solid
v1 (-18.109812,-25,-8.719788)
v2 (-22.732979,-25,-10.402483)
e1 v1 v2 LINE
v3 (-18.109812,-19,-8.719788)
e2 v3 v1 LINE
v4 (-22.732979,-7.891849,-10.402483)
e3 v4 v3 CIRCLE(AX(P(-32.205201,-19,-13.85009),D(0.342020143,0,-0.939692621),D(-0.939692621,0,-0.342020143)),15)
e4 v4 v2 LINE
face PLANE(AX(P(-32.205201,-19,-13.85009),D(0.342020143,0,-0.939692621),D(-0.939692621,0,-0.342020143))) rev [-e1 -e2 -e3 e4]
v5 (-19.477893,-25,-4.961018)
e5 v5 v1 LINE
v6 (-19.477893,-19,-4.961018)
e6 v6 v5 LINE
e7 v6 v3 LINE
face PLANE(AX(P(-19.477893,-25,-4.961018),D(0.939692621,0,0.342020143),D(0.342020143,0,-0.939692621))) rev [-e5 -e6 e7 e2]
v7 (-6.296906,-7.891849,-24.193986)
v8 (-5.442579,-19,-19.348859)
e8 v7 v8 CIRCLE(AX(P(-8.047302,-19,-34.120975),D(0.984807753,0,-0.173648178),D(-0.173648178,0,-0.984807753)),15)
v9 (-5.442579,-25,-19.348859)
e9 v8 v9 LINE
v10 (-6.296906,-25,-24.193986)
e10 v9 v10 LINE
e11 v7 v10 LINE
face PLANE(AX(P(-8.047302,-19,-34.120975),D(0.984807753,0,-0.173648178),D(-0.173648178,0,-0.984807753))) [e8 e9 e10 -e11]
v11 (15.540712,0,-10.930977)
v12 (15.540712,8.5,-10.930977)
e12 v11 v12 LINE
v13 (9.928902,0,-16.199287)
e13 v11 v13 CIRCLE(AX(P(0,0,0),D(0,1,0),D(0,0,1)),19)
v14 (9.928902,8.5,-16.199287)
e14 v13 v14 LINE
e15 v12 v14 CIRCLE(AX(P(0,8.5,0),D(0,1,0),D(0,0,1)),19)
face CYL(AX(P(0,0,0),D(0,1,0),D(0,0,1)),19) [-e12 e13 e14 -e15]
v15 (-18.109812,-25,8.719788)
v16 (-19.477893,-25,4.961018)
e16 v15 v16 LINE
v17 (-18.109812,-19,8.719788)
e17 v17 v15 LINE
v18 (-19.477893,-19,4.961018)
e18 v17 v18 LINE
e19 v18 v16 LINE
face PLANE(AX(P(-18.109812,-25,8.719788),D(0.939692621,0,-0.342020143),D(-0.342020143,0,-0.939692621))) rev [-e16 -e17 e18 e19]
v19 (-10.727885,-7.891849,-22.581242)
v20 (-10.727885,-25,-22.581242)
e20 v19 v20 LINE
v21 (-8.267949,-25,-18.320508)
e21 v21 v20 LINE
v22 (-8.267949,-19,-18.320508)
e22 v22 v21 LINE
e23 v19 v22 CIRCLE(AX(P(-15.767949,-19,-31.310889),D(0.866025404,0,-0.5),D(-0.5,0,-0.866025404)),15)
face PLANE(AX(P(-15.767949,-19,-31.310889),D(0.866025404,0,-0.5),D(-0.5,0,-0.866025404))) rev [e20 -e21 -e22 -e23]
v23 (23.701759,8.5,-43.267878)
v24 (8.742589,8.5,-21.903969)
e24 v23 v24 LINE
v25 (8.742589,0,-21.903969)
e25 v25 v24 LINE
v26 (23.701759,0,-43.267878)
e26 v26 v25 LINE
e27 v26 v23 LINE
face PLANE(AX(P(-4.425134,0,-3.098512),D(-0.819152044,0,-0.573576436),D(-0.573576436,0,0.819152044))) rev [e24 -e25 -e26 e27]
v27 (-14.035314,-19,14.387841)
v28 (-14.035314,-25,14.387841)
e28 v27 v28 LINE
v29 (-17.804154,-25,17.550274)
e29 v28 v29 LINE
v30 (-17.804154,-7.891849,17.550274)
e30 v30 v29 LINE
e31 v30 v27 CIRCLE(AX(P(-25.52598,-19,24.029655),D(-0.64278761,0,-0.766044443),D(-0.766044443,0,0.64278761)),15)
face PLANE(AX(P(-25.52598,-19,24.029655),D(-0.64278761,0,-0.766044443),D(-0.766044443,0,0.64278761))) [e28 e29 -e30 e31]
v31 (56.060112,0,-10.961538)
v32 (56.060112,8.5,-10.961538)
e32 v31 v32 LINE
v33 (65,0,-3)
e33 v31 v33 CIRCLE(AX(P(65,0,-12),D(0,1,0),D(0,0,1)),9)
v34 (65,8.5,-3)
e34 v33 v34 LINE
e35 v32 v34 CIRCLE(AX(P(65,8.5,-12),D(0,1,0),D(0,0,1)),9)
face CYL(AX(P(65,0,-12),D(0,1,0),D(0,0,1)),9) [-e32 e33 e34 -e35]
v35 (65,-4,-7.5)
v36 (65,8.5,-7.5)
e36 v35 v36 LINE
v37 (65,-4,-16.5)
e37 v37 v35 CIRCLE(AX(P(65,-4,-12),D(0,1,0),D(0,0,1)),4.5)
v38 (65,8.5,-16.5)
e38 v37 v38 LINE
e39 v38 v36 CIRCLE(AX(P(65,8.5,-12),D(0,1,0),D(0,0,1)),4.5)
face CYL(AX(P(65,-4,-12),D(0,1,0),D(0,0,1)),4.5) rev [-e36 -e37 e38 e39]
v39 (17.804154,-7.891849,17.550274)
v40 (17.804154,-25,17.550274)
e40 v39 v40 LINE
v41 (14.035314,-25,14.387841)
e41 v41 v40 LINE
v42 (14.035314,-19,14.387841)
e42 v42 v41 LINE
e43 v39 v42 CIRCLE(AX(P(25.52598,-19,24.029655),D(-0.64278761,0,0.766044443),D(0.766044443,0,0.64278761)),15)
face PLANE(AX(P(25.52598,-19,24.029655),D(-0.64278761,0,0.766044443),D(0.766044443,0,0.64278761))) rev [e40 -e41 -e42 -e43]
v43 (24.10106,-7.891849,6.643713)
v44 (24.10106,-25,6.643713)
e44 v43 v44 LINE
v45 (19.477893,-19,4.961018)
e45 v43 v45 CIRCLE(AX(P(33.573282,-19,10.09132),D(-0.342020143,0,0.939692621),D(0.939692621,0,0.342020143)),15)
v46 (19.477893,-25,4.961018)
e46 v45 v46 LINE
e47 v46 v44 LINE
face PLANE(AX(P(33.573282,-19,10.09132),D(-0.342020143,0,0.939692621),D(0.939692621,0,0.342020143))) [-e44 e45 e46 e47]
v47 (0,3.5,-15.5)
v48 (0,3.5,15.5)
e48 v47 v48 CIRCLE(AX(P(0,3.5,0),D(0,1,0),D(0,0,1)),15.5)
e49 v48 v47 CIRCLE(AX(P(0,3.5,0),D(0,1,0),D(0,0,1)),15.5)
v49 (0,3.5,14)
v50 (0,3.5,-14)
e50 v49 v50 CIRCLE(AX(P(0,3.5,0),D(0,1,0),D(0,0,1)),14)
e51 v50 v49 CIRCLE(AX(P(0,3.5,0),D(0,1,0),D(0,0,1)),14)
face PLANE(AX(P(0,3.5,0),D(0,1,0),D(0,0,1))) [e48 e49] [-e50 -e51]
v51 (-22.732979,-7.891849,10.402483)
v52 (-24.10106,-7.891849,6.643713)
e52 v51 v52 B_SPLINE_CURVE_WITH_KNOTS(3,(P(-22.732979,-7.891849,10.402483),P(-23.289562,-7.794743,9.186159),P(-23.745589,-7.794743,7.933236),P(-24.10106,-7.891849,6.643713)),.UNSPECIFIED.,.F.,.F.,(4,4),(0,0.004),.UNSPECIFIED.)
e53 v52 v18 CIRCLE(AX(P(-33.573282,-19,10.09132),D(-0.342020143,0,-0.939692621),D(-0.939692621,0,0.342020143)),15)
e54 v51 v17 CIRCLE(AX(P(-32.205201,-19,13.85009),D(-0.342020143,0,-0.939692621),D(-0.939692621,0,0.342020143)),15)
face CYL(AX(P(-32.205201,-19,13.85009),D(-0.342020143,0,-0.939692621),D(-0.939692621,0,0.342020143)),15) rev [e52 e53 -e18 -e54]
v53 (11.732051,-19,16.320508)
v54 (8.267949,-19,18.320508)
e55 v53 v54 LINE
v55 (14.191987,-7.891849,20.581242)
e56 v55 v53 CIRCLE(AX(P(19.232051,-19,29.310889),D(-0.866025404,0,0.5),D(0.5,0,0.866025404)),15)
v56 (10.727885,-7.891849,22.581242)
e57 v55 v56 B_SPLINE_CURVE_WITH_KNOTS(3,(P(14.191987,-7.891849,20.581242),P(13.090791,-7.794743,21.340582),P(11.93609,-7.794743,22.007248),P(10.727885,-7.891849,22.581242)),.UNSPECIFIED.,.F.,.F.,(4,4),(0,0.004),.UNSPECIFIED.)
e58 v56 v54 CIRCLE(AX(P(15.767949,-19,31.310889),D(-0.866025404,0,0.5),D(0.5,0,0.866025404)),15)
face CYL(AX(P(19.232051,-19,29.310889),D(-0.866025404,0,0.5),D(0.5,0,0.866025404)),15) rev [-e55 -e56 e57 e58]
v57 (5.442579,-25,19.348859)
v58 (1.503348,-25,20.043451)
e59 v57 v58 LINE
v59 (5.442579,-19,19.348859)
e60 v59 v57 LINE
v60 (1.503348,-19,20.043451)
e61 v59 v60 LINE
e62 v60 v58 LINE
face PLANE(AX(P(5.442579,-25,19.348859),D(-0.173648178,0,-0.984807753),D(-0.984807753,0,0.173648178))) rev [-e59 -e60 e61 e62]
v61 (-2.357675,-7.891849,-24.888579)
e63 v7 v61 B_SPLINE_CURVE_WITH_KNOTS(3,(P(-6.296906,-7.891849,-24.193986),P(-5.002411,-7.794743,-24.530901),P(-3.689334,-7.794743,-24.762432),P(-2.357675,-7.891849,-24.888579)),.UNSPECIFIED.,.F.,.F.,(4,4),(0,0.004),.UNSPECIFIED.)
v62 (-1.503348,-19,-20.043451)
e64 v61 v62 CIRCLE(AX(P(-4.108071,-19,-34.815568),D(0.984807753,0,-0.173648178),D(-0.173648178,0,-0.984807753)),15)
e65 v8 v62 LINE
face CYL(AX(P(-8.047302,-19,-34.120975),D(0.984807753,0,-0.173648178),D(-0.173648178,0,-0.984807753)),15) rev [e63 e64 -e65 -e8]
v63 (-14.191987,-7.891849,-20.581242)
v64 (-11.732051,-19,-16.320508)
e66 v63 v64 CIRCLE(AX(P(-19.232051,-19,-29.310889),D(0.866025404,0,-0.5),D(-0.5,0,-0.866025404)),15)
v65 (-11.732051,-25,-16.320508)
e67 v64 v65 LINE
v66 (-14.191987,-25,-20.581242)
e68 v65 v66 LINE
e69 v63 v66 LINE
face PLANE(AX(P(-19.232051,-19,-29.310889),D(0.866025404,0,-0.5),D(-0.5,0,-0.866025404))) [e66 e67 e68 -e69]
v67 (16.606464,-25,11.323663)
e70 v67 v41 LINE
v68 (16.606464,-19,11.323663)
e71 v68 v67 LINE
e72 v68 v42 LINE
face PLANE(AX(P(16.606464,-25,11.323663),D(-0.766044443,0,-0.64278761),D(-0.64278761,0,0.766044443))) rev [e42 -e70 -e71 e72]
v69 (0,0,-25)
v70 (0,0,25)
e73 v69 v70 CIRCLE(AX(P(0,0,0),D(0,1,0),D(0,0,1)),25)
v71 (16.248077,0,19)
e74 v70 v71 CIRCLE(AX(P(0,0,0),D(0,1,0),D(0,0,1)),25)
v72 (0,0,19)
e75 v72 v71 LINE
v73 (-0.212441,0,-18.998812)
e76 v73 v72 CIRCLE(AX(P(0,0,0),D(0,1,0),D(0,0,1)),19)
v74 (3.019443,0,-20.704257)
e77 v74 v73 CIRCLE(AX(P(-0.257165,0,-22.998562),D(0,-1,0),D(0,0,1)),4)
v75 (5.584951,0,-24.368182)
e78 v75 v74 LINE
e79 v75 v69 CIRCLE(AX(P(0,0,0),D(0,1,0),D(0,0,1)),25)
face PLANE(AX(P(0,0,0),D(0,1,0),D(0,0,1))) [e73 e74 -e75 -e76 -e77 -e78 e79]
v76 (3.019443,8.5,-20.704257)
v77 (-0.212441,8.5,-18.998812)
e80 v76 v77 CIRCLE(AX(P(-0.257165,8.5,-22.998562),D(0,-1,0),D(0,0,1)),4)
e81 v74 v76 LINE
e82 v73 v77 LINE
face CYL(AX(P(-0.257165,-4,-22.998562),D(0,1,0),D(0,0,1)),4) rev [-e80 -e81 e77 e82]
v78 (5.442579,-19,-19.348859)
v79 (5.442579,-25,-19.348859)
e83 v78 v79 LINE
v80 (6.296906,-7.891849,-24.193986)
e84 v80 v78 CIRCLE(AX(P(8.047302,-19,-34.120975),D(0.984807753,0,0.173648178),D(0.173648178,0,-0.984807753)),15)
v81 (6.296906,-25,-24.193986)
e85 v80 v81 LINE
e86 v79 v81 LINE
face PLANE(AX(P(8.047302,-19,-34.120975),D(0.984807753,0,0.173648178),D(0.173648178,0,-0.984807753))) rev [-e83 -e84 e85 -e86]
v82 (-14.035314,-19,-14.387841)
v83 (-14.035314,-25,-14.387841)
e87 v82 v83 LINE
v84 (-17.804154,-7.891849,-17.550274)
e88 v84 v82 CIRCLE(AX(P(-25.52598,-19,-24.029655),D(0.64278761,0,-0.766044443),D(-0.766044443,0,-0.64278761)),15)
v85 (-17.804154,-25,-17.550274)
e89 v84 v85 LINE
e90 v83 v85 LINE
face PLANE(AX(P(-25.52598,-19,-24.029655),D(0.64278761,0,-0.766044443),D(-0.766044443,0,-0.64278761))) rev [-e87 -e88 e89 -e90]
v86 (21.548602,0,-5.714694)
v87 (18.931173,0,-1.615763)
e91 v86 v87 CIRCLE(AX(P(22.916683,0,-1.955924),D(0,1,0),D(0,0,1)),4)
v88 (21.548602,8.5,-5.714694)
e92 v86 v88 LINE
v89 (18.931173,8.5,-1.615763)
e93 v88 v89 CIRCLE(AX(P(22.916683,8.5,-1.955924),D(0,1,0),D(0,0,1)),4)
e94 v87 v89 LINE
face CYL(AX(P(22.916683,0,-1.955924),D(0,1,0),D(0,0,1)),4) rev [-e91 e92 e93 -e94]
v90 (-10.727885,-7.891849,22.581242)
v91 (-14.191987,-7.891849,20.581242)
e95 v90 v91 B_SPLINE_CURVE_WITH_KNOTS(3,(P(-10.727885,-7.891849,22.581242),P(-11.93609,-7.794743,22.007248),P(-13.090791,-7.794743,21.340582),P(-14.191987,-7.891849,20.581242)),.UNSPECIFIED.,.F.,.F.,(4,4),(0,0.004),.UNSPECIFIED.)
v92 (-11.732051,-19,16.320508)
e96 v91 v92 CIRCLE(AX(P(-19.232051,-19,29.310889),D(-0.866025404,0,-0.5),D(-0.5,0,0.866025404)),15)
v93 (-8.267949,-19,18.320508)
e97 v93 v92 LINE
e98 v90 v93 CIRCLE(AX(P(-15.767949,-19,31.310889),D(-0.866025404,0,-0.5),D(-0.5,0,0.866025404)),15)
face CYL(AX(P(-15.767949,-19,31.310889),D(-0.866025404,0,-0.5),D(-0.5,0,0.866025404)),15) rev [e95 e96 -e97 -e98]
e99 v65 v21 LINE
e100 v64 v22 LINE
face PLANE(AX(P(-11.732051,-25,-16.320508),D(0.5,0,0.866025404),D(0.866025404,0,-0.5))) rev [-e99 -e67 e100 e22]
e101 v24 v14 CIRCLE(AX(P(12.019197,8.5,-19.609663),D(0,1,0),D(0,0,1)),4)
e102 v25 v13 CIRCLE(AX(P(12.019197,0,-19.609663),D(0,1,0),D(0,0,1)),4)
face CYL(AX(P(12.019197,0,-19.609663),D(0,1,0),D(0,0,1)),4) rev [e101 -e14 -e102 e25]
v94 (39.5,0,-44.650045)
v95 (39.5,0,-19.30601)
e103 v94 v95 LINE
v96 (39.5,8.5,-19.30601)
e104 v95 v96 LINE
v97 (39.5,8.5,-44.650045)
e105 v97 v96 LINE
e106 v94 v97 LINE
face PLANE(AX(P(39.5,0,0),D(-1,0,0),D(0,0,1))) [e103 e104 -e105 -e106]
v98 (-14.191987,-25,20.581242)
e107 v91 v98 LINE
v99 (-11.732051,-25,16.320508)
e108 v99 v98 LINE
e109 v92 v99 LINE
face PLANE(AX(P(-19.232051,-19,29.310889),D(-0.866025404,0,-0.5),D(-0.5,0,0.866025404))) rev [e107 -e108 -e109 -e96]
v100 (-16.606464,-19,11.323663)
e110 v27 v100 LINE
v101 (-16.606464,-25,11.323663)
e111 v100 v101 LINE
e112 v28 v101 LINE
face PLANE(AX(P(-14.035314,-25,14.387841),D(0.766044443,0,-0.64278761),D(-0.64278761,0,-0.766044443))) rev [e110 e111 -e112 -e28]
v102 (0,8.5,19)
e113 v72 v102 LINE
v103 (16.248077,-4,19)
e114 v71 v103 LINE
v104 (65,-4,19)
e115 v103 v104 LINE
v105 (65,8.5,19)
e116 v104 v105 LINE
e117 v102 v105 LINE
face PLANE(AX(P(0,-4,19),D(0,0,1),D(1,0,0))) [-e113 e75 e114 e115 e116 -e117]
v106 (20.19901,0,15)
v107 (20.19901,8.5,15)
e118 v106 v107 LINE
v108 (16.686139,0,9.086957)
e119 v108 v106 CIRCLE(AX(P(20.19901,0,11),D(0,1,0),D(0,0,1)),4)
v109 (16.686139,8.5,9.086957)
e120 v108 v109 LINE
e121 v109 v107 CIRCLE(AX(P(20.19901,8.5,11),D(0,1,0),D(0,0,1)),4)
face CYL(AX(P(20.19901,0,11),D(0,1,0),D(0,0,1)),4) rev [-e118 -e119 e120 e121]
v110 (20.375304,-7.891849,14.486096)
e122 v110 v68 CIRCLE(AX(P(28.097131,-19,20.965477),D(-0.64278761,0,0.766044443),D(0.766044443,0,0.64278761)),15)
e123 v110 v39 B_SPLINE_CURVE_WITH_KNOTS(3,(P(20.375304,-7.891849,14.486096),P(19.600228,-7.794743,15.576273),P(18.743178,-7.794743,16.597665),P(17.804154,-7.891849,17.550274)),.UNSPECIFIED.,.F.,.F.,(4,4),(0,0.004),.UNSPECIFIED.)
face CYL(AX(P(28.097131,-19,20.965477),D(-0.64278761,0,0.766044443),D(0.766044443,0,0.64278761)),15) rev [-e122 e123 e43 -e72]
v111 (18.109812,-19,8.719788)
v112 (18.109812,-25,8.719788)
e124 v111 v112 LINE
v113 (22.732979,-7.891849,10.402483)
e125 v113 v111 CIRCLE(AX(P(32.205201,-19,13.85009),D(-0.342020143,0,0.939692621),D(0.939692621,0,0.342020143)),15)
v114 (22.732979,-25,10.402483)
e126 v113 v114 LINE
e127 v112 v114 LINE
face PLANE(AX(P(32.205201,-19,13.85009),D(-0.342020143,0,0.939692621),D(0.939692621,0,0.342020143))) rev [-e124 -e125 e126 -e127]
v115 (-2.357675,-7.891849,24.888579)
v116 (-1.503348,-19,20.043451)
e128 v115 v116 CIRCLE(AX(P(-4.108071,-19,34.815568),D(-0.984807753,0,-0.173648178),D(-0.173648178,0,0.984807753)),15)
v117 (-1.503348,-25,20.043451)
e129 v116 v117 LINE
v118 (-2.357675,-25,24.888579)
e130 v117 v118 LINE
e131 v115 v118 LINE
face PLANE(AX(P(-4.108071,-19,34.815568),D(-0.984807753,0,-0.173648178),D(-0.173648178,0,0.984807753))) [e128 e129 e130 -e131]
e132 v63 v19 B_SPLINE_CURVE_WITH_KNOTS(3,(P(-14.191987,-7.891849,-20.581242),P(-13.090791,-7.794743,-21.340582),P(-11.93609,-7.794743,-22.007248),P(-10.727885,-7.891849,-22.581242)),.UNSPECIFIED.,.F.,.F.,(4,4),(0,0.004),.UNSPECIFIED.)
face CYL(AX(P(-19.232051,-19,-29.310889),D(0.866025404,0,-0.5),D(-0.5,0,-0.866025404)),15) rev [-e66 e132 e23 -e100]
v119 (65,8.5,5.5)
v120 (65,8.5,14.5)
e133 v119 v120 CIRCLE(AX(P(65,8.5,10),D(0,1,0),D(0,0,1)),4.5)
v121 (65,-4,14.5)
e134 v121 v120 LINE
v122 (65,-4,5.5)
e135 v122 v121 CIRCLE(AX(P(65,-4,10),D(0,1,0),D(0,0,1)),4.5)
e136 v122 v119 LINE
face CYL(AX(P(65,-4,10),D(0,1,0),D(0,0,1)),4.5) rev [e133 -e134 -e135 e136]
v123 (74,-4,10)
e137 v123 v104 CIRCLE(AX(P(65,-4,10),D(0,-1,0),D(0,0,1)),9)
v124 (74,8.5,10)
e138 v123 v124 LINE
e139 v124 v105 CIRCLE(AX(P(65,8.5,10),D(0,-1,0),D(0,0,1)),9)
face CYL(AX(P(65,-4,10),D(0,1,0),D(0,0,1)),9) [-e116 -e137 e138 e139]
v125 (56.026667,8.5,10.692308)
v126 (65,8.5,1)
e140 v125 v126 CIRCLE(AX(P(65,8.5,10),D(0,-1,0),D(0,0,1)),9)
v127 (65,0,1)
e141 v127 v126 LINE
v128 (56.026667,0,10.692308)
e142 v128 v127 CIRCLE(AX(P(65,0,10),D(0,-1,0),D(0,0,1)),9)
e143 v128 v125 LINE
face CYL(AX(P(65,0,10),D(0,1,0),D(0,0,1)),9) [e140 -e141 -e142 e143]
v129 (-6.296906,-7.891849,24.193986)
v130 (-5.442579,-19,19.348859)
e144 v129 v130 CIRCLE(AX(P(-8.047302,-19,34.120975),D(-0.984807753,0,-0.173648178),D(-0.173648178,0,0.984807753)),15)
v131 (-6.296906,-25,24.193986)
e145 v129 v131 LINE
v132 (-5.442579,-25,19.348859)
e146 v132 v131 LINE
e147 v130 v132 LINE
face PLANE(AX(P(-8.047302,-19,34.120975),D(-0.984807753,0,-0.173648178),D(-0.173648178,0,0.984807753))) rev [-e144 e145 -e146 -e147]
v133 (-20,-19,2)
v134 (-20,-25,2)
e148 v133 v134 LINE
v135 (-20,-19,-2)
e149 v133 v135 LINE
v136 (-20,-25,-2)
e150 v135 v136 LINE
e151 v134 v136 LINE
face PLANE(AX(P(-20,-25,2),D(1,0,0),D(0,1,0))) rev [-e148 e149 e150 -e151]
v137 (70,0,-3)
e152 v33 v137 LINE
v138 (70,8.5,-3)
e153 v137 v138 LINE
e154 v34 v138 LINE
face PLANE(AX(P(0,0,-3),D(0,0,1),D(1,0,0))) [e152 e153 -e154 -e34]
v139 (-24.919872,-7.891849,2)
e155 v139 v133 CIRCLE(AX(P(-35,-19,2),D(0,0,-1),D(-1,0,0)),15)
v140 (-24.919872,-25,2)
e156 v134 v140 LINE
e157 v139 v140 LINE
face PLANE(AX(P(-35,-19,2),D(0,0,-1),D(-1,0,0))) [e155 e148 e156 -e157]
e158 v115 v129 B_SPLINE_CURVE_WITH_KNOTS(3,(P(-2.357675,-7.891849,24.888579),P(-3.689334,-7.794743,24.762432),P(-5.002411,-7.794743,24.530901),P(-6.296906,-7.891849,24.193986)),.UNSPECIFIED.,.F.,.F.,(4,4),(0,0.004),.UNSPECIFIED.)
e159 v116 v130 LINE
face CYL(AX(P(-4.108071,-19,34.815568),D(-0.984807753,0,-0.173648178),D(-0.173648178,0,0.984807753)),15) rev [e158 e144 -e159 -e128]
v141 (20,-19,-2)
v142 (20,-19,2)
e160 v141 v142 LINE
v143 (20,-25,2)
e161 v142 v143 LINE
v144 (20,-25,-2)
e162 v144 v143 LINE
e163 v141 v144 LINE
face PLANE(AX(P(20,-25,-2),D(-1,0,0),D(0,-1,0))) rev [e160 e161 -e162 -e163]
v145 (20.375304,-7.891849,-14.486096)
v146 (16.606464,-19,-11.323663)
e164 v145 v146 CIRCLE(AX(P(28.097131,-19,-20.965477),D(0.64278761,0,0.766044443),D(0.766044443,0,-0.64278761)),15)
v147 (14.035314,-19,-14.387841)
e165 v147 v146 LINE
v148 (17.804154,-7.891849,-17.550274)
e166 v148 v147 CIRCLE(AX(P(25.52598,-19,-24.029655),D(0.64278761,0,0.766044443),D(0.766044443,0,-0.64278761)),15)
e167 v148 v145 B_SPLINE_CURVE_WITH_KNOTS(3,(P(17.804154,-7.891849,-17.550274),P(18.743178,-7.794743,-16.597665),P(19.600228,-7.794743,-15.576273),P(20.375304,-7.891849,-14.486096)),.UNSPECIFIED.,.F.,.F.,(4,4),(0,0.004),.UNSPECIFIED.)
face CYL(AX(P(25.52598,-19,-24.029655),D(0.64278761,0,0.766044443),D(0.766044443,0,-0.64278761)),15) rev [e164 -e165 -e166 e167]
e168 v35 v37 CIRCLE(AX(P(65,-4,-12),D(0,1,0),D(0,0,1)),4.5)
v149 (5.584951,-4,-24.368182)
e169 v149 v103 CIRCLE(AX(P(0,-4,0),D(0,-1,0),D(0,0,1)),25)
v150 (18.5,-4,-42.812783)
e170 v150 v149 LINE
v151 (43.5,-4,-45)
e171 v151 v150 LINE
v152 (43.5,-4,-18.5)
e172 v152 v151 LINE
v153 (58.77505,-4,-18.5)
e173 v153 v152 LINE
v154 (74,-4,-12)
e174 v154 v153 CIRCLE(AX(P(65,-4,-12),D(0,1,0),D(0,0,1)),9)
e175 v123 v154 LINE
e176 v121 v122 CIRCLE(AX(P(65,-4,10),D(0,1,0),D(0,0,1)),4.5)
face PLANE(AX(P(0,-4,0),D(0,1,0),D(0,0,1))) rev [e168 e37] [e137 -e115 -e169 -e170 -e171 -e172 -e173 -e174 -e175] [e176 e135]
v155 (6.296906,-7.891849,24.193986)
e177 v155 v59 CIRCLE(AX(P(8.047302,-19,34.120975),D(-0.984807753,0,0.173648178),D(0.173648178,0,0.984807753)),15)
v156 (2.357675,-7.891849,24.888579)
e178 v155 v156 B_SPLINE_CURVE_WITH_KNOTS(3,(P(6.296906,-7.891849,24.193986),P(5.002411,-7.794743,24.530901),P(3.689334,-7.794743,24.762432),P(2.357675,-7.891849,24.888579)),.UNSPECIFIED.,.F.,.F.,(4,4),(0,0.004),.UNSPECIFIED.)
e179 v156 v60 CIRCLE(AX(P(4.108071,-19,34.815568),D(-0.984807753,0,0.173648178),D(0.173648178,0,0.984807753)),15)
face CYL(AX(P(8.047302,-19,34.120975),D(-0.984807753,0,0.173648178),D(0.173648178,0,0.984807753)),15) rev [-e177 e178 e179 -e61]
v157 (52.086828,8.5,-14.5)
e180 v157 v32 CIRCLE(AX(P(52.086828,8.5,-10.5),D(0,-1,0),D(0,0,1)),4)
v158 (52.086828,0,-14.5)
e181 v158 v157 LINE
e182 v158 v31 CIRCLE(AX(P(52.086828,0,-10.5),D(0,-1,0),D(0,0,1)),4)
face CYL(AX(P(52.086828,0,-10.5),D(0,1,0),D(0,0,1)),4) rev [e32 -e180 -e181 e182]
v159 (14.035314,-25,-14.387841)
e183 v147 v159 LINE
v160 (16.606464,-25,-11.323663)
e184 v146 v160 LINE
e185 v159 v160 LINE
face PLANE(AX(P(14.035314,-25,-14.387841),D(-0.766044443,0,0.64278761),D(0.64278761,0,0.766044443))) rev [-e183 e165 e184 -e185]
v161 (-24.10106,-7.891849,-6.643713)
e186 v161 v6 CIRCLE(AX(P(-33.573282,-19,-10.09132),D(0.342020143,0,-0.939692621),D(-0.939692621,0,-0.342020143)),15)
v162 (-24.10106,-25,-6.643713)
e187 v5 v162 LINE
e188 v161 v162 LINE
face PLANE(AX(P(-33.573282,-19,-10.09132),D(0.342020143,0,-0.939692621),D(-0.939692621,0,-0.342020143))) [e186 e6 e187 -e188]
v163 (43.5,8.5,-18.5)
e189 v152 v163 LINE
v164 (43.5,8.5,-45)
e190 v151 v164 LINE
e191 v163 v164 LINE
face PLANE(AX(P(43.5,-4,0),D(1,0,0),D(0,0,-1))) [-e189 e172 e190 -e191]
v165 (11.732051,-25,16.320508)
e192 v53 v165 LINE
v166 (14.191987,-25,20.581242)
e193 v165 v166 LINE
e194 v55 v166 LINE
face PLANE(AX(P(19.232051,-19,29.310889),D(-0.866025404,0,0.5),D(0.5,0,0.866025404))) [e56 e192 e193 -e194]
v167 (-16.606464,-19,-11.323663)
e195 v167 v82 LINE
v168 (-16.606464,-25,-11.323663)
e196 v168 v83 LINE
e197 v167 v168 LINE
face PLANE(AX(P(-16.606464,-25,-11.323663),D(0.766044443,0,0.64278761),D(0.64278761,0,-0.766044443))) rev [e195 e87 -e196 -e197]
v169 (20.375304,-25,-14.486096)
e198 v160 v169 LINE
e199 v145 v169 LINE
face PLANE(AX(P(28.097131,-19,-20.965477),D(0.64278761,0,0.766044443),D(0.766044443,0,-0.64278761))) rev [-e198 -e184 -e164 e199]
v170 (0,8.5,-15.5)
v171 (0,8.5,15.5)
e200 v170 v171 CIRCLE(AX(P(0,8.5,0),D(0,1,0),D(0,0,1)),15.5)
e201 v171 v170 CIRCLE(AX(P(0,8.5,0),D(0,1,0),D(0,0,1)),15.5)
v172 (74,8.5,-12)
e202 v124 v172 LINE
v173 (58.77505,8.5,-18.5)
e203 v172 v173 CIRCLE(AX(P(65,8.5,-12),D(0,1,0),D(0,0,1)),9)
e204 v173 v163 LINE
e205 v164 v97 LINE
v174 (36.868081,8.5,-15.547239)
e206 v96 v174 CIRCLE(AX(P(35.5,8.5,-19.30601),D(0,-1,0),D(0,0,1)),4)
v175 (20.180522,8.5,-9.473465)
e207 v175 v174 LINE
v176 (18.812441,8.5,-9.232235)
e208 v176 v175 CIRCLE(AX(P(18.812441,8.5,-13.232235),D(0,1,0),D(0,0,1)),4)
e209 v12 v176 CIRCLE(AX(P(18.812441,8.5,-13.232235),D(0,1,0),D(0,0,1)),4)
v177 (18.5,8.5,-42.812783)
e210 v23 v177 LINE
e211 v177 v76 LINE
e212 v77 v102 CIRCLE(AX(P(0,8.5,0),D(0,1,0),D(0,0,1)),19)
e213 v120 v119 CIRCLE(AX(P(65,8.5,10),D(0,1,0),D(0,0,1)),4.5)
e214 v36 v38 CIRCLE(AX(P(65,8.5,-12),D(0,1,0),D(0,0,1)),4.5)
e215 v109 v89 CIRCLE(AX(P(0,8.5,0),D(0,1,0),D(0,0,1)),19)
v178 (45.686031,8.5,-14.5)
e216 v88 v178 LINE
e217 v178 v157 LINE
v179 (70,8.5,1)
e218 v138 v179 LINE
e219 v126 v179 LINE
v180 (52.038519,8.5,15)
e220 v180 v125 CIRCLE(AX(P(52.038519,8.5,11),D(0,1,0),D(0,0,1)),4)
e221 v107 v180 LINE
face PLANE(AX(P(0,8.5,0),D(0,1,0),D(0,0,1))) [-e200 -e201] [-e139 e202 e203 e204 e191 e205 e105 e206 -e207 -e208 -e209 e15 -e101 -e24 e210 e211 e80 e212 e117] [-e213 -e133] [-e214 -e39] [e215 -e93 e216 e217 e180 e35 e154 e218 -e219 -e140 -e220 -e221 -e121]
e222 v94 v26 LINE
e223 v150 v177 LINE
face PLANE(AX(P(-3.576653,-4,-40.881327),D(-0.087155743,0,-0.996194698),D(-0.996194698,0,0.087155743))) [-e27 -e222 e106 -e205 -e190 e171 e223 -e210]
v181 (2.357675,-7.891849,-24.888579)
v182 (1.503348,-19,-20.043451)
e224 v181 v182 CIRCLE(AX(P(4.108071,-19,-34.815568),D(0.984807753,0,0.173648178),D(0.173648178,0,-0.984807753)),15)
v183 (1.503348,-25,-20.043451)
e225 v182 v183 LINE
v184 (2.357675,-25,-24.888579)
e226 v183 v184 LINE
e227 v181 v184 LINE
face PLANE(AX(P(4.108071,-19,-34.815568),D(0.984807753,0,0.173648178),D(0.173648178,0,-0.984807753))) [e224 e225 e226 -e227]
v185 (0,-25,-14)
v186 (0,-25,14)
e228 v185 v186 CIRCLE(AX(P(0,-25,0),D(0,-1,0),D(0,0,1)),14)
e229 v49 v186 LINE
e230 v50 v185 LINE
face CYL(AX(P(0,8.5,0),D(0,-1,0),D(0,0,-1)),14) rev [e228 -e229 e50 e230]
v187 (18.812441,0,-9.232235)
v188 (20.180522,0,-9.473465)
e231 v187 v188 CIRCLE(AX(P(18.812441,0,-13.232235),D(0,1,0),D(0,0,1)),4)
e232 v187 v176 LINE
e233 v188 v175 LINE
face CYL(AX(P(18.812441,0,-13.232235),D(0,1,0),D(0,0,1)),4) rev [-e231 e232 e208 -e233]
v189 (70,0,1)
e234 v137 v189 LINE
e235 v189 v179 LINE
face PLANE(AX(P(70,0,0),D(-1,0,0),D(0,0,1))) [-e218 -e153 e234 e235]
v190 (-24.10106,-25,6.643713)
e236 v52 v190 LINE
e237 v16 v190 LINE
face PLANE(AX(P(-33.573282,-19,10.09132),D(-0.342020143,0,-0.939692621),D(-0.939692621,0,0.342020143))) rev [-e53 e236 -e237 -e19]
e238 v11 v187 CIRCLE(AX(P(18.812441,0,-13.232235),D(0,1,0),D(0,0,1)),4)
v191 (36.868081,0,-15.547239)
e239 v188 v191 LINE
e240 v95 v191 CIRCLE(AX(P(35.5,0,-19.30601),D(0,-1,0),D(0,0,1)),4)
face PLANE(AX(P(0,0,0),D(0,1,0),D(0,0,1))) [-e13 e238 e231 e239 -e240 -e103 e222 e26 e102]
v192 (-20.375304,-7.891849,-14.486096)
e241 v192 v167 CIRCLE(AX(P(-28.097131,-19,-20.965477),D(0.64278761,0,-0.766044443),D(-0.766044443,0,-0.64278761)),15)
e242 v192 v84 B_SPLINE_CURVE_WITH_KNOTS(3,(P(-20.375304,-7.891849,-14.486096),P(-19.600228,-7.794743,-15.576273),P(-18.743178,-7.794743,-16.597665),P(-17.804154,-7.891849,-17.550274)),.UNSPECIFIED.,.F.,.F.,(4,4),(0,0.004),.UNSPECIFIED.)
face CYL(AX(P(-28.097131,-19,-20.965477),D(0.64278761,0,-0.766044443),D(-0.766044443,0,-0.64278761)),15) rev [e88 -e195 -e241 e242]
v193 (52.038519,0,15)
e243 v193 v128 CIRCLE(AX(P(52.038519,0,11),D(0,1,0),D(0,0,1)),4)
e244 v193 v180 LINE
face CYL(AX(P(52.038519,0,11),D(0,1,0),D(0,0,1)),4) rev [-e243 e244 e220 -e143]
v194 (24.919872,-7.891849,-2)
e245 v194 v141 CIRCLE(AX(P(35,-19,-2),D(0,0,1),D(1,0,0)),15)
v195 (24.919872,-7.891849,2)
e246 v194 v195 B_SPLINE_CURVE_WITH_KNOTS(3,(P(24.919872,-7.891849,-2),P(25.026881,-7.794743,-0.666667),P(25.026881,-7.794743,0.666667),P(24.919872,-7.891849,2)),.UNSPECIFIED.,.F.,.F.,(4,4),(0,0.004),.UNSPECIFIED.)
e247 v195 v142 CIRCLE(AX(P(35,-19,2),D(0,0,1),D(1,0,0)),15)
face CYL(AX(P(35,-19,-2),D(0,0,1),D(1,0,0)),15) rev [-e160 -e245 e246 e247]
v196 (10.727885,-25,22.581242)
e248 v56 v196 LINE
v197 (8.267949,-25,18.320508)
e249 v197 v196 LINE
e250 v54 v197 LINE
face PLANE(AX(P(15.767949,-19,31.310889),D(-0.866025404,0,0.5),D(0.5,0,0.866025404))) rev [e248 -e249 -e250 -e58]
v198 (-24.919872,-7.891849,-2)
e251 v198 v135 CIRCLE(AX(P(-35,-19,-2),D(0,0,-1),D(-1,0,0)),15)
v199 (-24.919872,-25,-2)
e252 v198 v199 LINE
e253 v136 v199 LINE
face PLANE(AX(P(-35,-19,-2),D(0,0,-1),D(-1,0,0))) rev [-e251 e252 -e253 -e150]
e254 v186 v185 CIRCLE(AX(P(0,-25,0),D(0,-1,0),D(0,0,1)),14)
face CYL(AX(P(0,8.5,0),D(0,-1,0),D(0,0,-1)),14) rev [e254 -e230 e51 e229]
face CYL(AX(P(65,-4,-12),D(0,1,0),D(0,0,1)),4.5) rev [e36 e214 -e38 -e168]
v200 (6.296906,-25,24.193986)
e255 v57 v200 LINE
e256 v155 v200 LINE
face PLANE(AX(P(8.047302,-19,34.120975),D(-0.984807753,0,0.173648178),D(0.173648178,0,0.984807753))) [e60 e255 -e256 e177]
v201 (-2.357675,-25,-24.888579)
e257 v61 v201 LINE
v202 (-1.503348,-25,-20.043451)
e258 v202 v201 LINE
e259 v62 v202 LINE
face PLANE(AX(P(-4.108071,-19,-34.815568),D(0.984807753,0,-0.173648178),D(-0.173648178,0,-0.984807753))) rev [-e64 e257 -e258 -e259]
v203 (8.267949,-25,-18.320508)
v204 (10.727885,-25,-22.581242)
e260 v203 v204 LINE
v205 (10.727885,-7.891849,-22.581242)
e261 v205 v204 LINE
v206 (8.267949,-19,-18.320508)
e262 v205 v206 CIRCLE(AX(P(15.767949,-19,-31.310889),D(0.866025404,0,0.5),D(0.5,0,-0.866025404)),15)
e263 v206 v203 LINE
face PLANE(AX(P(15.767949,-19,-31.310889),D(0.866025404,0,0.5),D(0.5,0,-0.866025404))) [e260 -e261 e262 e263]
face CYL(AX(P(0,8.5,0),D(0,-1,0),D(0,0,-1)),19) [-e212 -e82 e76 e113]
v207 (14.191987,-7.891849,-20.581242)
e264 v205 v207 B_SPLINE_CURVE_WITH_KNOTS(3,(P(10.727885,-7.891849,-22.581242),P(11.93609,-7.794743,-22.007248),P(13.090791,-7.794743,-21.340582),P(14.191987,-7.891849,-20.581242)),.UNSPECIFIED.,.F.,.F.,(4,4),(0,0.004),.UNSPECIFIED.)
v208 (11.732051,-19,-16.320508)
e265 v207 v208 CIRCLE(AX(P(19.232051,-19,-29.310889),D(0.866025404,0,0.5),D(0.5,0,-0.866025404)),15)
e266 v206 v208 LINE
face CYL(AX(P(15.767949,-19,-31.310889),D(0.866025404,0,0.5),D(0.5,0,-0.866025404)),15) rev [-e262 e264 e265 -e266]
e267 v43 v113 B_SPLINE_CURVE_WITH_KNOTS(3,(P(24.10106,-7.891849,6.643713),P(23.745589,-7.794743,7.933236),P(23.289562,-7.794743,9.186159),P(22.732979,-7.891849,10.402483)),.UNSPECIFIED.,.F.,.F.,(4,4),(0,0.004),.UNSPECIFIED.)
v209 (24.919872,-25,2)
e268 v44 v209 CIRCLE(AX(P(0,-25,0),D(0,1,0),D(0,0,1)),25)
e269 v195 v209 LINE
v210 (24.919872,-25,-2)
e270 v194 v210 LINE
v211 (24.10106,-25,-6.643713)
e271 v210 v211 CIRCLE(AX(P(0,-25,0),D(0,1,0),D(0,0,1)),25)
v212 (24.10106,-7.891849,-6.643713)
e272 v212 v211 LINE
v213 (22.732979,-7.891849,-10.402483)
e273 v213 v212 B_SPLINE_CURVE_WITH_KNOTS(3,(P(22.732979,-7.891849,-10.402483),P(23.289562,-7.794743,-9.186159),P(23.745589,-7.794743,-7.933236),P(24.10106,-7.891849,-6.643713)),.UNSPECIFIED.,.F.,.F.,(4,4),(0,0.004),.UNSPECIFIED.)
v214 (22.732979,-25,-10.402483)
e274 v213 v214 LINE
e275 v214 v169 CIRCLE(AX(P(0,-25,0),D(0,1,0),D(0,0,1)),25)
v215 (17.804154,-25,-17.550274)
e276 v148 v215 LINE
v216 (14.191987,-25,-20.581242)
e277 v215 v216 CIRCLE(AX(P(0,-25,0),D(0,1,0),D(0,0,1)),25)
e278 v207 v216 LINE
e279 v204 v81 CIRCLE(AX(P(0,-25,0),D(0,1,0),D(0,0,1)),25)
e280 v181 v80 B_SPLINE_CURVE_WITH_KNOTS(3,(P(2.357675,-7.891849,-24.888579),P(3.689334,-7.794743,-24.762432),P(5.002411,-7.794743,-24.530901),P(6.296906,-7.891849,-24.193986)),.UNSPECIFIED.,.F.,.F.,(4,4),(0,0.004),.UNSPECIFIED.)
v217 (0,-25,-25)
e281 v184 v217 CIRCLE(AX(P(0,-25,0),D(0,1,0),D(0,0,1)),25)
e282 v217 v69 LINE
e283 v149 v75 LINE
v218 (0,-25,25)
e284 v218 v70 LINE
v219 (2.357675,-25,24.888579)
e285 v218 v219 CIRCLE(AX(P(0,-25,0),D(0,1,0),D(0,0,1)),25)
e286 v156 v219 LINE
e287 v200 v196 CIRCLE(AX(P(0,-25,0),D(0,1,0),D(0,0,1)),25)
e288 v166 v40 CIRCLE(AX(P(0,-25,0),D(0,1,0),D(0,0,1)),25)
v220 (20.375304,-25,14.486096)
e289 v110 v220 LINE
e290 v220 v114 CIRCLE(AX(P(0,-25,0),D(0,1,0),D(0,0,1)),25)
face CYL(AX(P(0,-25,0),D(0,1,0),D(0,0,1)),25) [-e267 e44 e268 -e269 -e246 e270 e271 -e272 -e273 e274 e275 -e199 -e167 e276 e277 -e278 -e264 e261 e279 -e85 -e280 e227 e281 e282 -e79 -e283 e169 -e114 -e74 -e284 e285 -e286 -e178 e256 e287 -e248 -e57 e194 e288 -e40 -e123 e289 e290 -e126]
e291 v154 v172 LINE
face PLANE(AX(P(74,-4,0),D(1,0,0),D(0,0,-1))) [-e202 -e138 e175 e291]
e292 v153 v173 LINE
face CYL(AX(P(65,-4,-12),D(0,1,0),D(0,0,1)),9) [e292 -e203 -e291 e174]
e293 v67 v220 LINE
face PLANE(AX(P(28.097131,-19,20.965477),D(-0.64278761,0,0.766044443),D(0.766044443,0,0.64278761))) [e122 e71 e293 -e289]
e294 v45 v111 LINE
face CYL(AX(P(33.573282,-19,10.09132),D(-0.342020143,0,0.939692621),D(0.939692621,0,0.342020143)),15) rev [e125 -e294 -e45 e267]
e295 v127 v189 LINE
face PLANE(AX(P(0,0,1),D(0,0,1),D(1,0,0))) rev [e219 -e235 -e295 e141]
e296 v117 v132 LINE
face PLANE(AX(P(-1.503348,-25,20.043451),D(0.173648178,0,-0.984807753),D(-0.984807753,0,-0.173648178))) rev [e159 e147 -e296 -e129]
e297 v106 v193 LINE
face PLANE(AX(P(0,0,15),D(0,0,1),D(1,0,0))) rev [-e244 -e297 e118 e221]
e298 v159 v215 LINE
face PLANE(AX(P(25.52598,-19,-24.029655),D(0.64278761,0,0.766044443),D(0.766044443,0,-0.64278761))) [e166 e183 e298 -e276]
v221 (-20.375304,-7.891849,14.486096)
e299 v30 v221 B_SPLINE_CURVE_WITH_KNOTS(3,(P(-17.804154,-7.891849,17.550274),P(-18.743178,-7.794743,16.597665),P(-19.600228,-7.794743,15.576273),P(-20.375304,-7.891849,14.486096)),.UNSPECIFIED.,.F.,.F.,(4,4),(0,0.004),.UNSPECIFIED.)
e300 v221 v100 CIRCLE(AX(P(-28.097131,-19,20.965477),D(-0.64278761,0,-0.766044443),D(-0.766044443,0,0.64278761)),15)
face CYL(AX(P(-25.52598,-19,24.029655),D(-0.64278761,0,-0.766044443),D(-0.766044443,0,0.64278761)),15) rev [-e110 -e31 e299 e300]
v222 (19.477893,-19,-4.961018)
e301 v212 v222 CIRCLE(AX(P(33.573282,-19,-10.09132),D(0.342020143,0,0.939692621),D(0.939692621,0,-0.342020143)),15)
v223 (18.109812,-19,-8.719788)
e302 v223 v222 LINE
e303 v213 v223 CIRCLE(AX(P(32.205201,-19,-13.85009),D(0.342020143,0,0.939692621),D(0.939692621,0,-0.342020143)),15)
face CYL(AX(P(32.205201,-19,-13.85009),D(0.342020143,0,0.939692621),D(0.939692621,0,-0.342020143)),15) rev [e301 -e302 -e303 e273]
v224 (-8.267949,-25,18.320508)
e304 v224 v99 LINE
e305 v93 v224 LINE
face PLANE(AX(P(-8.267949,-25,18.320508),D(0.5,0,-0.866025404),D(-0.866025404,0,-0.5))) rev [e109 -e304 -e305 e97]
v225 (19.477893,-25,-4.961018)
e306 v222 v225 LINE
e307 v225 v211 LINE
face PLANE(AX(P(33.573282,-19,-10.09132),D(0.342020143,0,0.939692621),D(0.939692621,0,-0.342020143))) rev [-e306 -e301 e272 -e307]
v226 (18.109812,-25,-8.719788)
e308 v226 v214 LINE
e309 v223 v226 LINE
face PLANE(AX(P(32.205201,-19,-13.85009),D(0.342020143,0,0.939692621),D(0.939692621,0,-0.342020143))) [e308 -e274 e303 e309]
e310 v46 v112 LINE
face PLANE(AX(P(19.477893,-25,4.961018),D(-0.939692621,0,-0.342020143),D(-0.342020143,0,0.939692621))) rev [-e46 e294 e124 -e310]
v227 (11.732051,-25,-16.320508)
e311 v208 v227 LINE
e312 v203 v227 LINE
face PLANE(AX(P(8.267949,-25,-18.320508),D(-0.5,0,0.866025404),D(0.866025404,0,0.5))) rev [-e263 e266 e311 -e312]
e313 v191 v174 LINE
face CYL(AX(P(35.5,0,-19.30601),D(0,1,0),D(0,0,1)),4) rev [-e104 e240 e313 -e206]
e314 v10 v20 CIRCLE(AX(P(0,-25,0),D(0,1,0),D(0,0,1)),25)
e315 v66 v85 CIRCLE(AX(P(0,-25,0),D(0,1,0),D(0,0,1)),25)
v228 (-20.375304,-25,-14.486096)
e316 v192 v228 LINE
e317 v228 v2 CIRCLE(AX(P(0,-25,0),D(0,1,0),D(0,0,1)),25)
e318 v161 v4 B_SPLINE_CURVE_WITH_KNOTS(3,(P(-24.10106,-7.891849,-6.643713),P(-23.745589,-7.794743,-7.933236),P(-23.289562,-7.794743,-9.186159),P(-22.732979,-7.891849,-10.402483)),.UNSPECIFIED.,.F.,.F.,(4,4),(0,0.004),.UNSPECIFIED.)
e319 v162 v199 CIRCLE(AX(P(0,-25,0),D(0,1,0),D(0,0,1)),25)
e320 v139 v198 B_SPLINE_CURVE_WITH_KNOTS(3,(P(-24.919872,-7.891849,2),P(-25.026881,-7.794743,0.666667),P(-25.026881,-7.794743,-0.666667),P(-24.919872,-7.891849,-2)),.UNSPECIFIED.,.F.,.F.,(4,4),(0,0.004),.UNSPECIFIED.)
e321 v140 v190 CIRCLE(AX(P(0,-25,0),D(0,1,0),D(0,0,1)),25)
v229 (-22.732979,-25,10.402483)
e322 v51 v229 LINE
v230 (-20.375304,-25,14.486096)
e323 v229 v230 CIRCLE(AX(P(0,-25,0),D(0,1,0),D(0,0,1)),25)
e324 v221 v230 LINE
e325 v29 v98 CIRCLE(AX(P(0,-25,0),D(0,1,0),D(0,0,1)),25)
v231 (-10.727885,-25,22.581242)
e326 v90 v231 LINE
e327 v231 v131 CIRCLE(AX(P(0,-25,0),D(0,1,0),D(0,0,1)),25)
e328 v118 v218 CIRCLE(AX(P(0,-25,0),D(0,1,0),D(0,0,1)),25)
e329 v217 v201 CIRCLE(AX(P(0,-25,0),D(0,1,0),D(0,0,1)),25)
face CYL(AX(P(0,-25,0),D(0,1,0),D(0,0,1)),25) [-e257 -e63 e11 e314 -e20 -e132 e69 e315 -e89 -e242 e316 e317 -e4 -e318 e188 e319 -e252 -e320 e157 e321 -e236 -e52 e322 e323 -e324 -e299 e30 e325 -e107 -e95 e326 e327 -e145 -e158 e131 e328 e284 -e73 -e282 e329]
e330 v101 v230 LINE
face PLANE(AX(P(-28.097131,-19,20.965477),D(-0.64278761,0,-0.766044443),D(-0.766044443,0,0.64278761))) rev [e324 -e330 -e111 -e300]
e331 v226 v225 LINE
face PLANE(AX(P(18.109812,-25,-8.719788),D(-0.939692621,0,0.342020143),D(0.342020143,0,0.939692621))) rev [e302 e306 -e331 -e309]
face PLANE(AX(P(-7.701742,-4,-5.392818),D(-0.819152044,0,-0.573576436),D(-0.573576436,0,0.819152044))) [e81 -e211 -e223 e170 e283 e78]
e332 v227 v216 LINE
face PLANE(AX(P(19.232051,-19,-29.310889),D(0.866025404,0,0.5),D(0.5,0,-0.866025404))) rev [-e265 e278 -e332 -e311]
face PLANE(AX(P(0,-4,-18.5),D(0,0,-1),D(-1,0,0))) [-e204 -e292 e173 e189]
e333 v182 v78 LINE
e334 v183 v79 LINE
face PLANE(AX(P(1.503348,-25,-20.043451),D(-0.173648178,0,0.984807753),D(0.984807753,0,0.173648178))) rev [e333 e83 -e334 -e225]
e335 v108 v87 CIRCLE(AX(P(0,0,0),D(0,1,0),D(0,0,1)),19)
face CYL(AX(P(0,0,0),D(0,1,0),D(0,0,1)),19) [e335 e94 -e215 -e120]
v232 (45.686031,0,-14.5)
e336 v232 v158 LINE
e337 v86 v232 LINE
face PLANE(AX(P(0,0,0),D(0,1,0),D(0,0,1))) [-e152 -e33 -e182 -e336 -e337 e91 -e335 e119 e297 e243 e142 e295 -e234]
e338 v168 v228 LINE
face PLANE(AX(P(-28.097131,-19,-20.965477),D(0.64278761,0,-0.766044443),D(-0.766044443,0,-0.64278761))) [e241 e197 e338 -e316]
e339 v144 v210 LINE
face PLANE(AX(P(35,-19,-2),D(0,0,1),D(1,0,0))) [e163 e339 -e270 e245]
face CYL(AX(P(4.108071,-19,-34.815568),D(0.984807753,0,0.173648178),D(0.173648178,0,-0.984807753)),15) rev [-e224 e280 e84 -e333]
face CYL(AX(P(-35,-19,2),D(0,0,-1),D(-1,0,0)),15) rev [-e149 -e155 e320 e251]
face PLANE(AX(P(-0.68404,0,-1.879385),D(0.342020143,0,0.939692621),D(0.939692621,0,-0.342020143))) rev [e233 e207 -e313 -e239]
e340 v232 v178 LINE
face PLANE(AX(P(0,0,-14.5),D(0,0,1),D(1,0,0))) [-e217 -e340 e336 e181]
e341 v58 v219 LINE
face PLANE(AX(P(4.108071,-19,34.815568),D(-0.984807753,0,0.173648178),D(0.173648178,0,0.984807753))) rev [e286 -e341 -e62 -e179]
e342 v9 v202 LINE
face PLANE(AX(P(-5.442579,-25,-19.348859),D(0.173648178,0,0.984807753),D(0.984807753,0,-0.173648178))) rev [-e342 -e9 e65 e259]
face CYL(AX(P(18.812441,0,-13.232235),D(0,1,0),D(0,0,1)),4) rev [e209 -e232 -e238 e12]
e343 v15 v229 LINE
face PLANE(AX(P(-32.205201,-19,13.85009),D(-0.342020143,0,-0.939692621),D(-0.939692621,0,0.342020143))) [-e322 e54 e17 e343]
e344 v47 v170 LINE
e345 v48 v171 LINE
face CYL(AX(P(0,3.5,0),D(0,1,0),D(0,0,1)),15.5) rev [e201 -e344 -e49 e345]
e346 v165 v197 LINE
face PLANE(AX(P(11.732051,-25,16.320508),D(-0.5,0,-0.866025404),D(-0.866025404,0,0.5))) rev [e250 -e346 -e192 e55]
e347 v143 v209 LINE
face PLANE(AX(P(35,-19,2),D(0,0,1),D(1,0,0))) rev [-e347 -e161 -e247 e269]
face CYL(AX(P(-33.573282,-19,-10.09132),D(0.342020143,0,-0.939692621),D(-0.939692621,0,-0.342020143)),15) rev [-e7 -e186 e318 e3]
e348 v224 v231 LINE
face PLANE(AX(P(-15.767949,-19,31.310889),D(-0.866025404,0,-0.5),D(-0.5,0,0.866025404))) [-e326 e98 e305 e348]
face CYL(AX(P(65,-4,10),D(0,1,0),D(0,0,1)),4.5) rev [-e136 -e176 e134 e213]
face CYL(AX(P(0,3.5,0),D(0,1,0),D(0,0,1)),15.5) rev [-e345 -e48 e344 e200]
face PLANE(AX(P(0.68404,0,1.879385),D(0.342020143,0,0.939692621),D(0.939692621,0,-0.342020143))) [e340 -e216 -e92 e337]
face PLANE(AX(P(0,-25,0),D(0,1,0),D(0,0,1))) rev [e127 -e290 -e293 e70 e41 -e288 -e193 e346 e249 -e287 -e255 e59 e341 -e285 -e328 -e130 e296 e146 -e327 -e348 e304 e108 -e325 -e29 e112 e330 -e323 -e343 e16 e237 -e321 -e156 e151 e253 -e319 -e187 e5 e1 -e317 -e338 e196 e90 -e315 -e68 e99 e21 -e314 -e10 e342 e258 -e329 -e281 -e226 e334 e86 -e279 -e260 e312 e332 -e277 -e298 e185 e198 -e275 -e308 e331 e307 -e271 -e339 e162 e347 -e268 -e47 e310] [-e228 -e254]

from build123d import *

# Parameters (mm, degrees)
HUB_SKETCH_50_R                   = 25
HUB_CYLINDER_50_DEPTH             = 25
UPPER_PAD_SKETCH_R                = 19
UPPER_PAD_SKETCH_R_2              = 14
UPPER_PAD_DEPTH                   = 8.5
HUB_CUT_REACH                     = 45.301
HUB_CUT_SKETCH_R                  = 14
HUB_RECESS_SKETCH_31_R            = 15.5
HUB_RECESS_31_DEPTH               = 5
LEVER_START                       = -12.5
LEVER_ARM_PROFILE_SKETCH_R        = 4.5
LEVER_ARM_DEPTH                   = 12.5
LEVER_START_2                     = -8.5
LEVER_ARM_POCKETS_AND_HOLES_DEPTH = 8.5
FIN_SLOT_DEPTH                    = 2
FIN_SLOT_PATTERN_18X_COUNT        = 18


with BuildPart() as part:
    # Hub Sketch _50 → Hub Cylinder _50 (new body)
    with BuildSketch(Plane(origin=(0, 0, 0), x_dir=(1, 0, 0), z_dir=(0, 1, 0))):
        with Locations(Location((0, 0, 0), (0, 0, 270))):
            Circle(HUB_SKETCH_50_R)
    extrude(amount=-HUB_CYLINDER_50_DEPTH)

    # Upper Pad Sketch → Upper Pad (add)
    with BuildSketch(Plane(origin=(0, 0, 0), x_dir=(1, 0, 0), z_dir=(0, 1, 0))):
        with Locations(Location((0, 0, 0), (0, 0, 270))):
            Circle(UPPER_PAD_SKETCH_R)
        with Locations(Location((0, 0, 0), (0, 0, 270))):
            Circle(UPPER_PAD_SKETCH_R_2, mode=Mode.SUBTRACT)
    extrude(amount=UPPER_PAD_DEPTH)

    # Hub Cut Sketch → Hub Cut (cut, up to next)
    with BuildSketch(Plane(origin=(0, 0, 0), x_dir=(1, 0, 0), z_dir=(0, 1, 0)), mode=Mode.PRIVATE) as hub_cut_sk1:
        with Locations(Location((0, 0, 0), (0, 0, 270))):
            Circle(HUB_CUT_SKETCH_R)
    hub_cut_tool1 = extrude(hub_cut_sk1.sketch, amount=-HUB_CUT_REACH, mode=Mode.PRIVATE) & part.part
    add(hub_cut_tool1.solids().sort_by_distance((0, 0, 0))[0], mode=Mode.SUBTRACT)

    # Hub Recess Sketch _31 → Hub Recess _31 (cut)
    with BuildSketch(Plane(origin=(0, 8.5, 0), x_dir=(1, 0, 0), z_dir=(0, 1, 0))):
        with Locations(Location((0, 0, 0), (0, 0, 270))):
            Circle(HUB_RECESS_SKETCH_31_R)
    extrude(amount=-HUB_RECESS_31_DEPTH, mode=Mode.SUBTRACT)

    # Lever Arm Profile Sketch → Lever Arm (add)
    with BuildSketch(Plane(origin=(0, 8.5, 0), x_dir=(1, 0, 0), z_dir=(0, 1, 0)).offset(LEVER_START)):
        with BuildLine():
            Line((0, -19), (65, -19))
            ThreePointArc((65, -19), (71.363961031, -16.363961031), (74, -10))
            Line((74, -10), (74, 12))
            ThreePointArc((74, 12), (68.53379766, 20.277214151), (58.775050201, 18.5))
            Line((58.775050201, 18.5), (43.5, 18.5))
            Line((43.5, 18.5), (43.5, 45))
            Line((43.5, 45), (18.5, 42.812783412))
            Line((18.5, 42.812783412), (3.019442807, 20.704256513))
            ThreePointArc((3.019442807, 20.704256513), (1.609636047, 19.460900253), (-0.212440958, 18.998812301))
            ThreePointArc((-0.212440958, 18.998812301), (18.999703073, 0.106222139), (0, -19))
        make_face()
        with Locations(Location((65, -10, 0), (0, 0, 270))):
            Circle(LEVER_ARM_PROFILE_SKETCH_R, mode=Mode.SUBTRACT)
        with Locations(Location((65, 12, 0), (0, 0, 270))):
            Circle(LEVER_ARM_PROFILE_SKETCH_R, mode=Mode.SUBTRACT)
    extrude(amount=LEVER_ARM_DEPTH)

    # Sketch5_3 → Lever Arm Pockets and Holes (cut)
    with BuildSketch(Plane(origin=(0, 8.5, 0), x_dir=(1, 0, 0), z_dir=(0, 1, 0)).offset(LEVER_START_2)):
        with BuildLine():
            ThreePointArc((19, 0), (18.412450045, -4.688462793), (16.686138594, -9.086956522))
            ThreePointArc((16.686138594, -9.086956522), (16.760102062, -13.043015674), (20.199009877, -15))
            Line((20.199009877, -15), (52.038518603, -15))
            ThreePointArc((52.038518603, -15), (54.973716146, -13.717464882), (56.026666725, -10.692307692))
            ThreePointArc((56.026666725, -10.692307692), (58.395805529, -3.885704016), (65, -1))
            Line((65, -1), (70, -1))
            Line((70, -1), (70, 3))
            Line((70, 3), (65, 3))
            ThreePointArc((65, 3), (59.014440454, 5.278908056), (56.06011199, 10.961538462))
            ThreePointArc((56.06011199, 10.961538462), (54.747077117, 13.487151975), (52.08682843, 14.5))
            Line((52.08682843, 14.5), (45.686031382, 14.5))
            Line((45.686031382, 14.5), (21.548602473, 5.714694345))
            ThreePointArc((21.548602473, 5.714694345), (19.545401033, 4.1087029), (18.931172951, 1.61576319))
            ThreePointArc((18.931172951, 1.61576319), (18.982785439, 0.808614224), (19, 0))
        make_face()
        with BuildLine():
            ThreePointArc((8.742589, 21.903969159), (8.102979357, 18.795269171), (9.928902016, 16.199287168))
            ThreePointArc((9.928902016, 16.199287168), (13.004387246, 13.852289066), (15.5407124, 10.930976996))
            ThreePointArc((15.5407124, 10.930976996), (17.613669166, 9.416092585), (20.1805219, 9.473464828))
            Line((20.1805219, 9.473464828), (36.868080573, 15.547239468))
            ThreePointArc((36.868080573, 15.547239468), (38.776608177, 17.011704206), (39.5, 19.306009951))
            Line((39.5, 19.306009951), (39.5, 44.650045346))
            Line((39.5, 44.650045346), (23.701759282, 43.267878379))
            Line((23.701759282, 43.267878379), (8.742589, 21.903969159))
        make_face()
    extrude(amount=LEVER_ARM_POCKETS_AND_HOLES_DEPTH, mode=Mode.SUBTRACT)

    # Fin Slot Sketch → Fin Slot (cut, symmetric)
    with BuildSketch(Plane.XY):
        with BuildLine():
            Line((20, -25), (20, -19))
            ThreePointArc((20, -19), (21.306936062, -12.876275643), (25, -7.819660113))
            Line((25, -7.819660113), (25, -25))
            Line((25, -25), (20, -25))
        make_face()
    fin_slot = extrude(amount=FIN_SLOT_DEPTH, both=True, mode=Mode.SUBTRACT)

    # Fin Slot Pattern 18x: Fin Slot ×18 about axis
    fin_slot_pattern_18x_axis = Axis((0, 0, 0), (0, 1, 0))
    for i in range(1, FIN_SLOT_PATTERN_18X_COUNT):
        add(fin_slot.rotate(fin_slot_pattern_18x_axis, i * 360 / FIN_SLOT_PATTERN_18X_COUNT), mode=Mode.SUBTRACT)


solid = part.part
